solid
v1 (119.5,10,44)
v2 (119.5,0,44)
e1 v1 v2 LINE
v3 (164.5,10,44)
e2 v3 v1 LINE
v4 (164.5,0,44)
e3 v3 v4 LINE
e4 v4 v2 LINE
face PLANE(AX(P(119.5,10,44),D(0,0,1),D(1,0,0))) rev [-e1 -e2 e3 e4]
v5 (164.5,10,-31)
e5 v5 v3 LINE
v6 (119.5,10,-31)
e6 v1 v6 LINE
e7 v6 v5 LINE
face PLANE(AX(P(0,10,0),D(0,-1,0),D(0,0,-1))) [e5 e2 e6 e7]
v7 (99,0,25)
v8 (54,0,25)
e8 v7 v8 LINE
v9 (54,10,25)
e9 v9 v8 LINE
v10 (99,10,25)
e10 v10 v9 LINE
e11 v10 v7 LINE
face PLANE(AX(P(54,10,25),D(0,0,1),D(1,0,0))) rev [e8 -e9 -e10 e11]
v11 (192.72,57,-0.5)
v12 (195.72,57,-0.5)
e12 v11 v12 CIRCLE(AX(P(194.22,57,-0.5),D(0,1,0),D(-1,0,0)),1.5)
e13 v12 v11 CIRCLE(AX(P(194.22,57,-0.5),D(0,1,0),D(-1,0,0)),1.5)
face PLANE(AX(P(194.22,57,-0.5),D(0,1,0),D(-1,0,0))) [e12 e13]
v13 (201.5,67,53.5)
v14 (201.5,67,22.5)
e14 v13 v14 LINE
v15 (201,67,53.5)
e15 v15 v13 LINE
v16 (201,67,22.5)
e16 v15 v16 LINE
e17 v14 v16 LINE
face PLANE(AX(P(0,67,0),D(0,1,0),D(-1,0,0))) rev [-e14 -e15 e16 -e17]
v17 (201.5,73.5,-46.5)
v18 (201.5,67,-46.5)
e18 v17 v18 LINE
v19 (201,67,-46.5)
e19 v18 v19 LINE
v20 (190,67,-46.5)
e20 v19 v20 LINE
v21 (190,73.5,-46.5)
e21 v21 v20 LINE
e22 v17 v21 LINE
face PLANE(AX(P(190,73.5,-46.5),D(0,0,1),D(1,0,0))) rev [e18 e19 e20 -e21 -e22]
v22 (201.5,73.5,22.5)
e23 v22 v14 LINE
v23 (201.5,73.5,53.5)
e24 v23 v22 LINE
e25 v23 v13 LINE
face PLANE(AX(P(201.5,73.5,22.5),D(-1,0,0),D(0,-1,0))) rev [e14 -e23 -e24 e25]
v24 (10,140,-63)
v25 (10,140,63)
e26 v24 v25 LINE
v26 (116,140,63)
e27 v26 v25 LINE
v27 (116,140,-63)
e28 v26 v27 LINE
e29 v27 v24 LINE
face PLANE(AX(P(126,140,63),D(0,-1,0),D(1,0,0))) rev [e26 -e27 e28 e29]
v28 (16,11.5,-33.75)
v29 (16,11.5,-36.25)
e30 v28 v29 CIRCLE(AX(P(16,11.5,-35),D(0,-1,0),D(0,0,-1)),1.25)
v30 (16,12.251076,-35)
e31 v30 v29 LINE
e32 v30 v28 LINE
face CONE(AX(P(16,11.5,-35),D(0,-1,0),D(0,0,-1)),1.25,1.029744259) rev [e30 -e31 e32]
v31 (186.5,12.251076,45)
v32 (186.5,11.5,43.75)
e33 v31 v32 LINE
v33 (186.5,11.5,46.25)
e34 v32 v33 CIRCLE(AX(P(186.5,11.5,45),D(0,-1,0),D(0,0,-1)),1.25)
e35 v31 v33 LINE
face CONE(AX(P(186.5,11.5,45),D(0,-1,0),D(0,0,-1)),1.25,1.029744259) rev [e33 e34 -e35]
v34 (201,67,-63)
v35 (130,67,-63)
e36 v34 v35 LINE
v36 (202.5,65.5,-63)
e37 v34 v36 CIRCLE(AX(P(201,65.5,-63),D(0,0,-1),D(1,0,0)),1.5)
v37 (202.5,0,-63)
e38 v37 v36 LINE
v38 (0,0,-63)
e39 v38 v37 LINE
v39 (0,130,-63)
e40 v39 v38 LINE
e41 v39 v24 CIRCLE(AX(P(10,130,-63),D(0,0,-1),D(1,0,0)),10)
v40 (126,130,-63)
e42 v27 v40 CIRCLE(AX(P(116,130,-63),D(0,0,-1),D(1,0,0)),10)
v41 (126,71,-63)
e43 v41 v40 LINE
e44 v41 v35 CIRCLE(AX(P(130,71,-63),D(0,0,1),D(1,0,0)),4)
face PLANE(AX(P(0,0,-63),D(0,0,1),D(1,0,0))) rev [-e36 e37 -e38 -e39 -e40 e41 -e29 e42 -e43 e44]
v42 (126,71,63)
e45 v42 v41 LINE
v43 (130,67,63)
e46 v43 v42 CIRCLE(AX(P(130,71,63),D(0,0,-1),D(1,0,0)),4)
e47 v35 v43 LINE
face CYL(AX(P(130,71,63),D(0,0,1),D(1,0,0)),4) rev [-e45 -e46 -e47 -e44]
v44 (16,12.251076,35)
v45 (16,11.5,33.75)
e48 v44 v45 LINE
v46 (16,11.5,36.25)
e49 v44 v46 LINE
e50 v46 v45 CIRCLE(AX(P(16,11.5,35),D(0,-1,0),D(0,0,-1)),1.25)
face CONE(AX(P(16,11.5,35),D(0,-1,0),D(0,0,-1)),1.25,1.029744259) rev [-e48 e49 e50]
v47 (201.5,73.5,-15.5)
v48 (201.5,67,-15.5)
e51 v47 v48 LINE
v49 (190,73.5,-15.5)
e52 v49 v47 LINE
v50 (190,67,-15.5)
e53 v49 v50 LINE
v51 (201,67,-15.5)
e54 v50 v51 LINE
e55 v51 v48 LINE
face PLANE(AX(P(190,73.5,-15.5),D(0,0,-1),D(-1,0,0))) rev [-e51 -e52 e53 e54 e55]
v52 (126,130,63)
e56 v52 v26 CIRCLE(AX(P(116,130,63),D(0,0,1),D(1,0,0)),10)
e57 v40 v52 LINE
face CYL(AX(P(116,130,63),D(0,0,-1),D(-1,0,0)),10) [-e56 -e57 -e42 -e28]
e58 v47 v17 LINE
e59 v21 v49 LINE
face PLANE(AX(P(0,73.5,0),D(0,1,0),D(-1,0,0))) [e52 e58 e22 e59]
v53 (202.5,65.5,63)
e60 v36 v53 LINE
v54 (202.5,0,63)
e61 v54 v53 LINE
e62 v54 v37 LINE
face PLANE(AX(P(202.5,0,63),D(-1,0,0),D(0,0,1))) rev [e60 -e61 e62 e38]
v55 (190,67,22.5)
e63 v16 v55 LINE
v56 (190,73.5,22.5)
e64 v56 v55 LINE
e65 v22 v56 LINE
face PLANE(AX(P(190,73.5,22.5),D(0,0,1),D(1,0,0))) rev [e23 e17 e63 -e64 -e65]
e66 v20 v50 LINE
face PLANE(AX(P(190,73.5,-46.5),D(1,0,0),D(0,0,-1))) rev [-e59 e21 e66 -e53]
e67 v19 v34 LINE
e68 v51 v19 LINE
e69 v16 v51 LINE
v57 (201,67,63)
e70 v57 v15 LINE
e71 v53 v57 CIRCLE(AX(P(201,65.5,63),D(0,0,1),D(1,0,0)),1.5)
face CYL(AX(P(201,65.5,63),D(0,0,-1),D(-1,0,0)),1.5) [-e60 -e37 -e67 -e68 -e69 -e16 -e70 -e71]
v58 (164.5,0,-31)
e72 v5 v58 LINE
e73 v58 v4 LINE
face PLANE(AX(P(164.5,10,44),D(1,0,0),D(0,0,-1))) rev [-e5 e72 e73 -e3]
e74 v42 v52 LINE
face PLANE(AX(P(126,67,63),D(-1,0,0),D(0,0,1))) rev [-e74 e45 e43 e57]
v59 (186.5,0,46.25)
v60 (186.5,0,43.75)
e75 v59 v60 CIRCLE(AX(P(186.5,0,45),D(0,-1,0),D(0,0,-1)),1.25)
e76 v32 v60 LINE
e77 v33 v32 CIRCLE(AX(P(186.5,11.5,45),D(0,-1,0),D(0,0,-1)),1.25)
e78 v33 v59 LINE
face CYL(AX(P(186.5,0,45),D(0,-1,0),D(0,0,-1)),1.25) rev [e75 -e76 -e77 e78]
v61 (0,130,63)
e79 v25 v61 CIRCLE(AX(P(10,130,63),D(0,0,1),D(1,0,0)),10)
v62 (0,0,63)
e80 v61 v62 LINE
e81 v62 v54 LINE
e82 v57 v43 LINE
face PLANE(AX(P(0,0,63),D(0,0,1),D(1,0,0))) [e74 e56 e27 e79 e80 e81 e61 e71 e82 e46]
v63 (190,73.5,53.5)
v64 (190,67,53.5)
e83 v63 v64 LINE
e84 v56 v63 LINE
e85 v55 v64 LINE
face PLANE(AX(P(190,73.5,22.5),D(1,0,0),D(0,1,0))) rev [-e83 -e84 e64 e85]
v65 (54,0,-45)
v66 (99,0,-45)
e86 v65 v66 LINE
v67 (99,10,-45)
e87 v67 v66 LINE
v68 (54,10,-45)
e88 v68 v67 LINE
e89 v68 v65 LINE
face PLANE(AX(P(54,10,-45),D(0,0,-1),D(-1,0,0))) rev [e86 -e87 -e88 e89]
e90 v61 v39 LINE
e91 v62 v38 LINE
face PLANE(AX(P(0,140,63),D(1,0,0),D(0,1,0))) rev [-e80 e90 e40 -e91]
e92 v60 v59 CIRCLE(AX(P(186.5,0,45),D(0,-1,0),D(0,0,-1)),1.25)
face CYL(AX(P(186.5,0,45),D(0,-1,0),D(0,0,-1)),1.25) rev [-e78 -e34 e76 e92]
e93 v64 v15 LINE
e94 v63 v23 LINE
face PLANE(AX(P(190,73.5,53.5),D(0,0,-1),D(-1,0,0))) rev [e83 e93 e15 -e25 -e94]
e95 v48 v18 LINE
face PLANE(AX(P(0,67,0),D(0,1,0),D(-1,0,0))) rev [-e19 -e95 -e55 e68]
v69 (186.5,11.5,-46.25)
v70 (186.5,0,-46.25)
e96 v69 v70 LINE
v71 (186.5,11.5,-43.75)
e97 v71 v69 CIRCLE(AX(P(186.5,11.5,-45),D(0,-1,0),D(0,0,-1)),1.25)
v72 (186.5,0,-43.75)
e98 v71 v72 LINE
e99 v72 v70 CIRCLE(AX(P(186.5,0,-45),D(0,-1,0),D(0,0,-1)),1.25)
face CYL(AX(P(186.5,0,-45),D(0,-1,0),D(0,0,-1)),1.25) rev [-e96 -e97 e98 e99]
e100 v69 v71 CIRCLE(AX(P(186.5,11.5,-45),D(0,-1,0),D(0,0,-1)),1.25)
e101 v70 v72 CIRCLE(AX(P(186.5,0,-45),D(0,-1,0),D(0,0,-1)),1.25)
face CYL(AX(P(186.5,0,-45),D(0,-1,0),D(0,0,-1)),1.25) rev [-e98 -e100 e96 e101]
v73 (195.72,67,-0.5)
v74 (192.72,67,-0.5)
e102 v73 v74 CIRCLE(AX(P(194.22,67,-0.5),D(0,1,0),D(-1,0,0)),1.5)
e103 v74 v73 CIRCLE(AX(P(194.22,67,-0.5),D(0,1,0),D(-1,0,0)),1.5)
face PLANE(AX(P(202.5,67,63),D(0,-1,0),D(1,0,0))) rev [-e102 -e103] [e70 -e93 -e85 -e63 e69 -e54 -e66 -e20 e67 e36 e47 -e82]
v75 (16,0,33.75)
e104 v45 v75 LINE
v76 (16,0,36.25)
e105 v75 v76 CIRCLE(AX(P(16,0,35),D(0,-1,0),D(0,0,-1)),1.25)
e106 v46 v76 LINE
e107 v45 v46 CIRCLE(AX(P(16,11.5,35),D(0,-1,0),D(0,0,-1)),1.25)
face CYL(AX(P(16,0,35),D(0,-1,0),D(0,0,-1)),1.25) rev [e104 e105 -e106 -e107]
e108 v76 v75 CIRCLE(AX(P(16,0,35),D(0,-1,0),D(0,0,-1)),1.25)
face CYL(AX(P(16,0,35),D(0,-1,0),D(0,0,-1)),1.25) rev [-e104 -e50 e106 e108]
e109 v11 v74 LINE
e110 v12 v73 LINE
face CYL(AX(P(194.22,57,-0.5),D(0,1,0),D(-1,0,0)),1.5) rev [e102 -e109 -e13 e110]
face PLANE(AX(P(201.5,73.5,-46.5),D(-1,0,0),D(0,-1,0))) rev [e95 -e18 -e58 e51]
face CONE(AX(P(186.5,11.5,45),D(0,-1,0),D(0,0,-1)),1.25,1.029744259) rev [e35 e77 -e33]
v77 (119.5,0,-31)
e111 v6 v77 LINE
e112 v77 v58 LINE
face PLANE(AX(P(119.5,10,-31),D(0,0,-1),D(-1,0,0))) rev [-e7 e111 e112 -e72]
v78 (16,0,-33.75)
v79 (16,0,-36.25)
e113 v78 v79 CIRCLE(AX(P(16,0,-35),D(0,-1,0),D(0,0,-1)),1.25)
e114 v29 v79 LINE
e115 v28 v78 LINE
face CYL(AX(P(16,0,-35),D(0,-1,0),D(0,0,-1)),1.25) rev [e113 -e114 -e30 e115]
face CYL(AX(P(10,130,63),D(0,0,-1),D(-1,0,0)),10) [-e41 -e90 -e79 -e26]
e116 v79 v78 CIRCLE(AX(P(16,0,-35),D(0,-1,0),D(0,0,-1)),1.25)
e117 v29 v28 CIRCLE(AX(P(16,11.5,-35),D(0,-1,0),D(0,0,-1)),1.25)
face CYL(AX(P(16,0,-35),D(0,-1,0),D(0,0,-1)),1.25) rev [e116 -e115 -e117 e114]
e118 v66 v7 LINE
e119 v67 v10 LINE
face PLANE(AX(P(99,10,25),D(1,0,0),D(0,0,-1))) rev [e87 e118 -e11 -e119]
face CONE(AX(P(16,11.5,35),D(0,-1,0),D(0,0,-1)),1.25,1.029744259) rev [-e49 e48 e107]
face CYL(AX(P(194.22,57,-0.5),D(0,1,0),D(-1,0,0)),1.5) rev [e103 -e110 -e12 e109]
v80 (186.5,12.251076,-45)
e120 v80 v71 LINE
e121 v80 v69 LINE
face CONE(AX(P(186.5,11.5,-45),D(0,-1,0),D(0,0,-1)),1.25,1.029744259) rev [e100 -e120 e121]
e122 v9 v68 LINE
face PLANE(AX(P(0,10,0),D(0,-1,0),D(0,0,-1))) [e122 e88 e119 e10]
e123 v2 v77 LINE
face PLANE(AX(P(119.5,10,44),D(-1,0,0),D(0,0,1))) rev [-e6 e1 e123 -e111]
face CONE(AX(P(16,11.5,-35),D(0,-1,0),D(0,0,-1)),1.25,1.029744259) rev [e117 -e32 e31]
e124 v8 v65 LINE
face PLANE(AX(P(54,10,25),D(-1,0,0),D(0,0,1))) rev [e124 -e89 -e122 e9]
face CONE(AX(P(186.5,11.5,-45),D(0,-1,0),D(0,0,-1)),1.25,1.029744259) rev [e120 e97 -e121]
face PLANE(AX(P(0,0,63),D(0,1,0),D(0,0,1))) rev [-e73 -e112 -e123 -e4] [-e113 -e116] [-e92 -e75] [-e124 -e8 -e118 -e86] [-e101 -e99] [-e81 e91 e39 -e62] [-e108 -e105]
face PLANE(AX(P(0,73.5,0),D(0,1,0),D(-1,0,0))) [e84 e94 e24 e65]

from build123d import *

# Parameters (mm, degrees)
EXTRUDE_1_DEPTH        = 63
FILLET_1_R             = 10
FILLET_2_R             = 1.5
SKETCH_2_R             = 1.5
CUT_EXTRUDE_1_DEPTH    = 10
SKETCH_3_W             = 11.5
SKETCH_3_H             = 31
EXTRUDE_2_DEPTH        = 6.5
FILLET_3_R             = 4
HOLE_WIZARD_M3_1_D     = 2.5
HOLE_WIZARD_M3_1_DEPTH = 11.5
HOLE_WIZARD_M3_1_TIP   = 0.751075774
SKETCH_6_W             = 45
SKETCH_6_H             = 70
SKETCH_6_H_2           = 75
CUT_EXTRUDE_2_DEPTH    = 10


with BuildPart() as part:
    # 草图1 → 凸台-拉伸1 (new, symmetric)
    with BuildSketch(Plane.XY):
        Polygon((0, 140), (0, 0), (202.5, 0), (202.5, 67), (126, 67), (126, 140), align=None)
    extrude(amount=EXTRUDE_1_DEPTH, both=True)

    # 圆角1
    fillet_1_edges = [part.edges().sort_by_distance(p)[0] for p in [
        (126, 140, 0),
        (0, 140, 0),
    ]]
    fillet(fillet_1_edges, radius=FILLET_1_R)

    # 圆角2
    fillet_2_edges = [part.edges().sort_by_distance(p)[0] for p in [
        (202.5, 67, 0),
    ]]
    fillet(fillet_2_edges, radius=FILLET_2_R)

    # 草图2 → 切除-拉伸1 (cut)
    with BuildSketch(Plane(origin=(0, 67, 0), x_dir=(1, 0, 0), z_dir=(0, 1, 0))):
        with Locations(Location((194.22, 0.5, 0), (0, 0, 180))):
            Circle(SKETCH_2_R)
    extrude(amount=-CUT_EXTRUDE_1_DEPTH, mode=Mode.SUBTRACT)

    # 草图3 → 凸台-拉伸2 (add)
    with BuildSketch(Plane(origin=(0, 67, 0), x_dir=(1, 0, 0), z_dir=(0, 1, 0))):
        with Locations((195.75, -38)):
            Rectangle(SKETCH_3_W, SKETCH_3_H)
        with Locations((195.75, 31)):
            Rectangle(SKETCH_3_W, SKETCH_3_H)
    extrude(amount=EXTRUDE_2_DEPTH)

    # 圆角3
    fillet_3_edges = [part.edges().sort_by_distance(p)[0] for p in [
        (126, 67, 0),
    ]]
    fillet(fillet_3_edges, radius=FILLET_3_R)

    # M3 螺纹孔1
    with Locations(Plane(origin=(0, 0, 0), x_dir=(-1, 0, 0), z_dir=(0, -1, 0))):
        with Locations((-16, -35), (-16, 35), (-186.5, -45), (-186.5, 45)):
            Hole(HOLE_WIZARD_M3_1_D / 2, depth=HOLE_WIZARD_M3_1_DEPTH)
            with Locations((0, 0, -(HOLE_WIZARD_M3_1_DEPTH + HOLE_WIZARD_M3_1_TIP / 2))):  # 118° drill point
                Cone(0, HOLE_WIZARD_M3_1_D / 2, HOLE_WIZARD_M3_1_TIP, mode=Mode.SUBTRACT)

    # 草图6 → 切除-拉伸2 (cut)
    with BuildSketch(Plane(origin=(0, 0, 0), x_dir=(-1, 0, 0), z_dir=(0, -1, 0))):
        with Locations((-76.5, 10)):
            Rectangle(SKETCH_6_W, SKETCH_6_H)
        with Locations((-142, -6.5)):
            Rectangle(SKETCH_6_W, SKETCH_6_H_2)
    extrude(amount=-CUT_EXTRUDE_2_DEPTH, mode=Mode.SUBTRACT)


solid = part.part
